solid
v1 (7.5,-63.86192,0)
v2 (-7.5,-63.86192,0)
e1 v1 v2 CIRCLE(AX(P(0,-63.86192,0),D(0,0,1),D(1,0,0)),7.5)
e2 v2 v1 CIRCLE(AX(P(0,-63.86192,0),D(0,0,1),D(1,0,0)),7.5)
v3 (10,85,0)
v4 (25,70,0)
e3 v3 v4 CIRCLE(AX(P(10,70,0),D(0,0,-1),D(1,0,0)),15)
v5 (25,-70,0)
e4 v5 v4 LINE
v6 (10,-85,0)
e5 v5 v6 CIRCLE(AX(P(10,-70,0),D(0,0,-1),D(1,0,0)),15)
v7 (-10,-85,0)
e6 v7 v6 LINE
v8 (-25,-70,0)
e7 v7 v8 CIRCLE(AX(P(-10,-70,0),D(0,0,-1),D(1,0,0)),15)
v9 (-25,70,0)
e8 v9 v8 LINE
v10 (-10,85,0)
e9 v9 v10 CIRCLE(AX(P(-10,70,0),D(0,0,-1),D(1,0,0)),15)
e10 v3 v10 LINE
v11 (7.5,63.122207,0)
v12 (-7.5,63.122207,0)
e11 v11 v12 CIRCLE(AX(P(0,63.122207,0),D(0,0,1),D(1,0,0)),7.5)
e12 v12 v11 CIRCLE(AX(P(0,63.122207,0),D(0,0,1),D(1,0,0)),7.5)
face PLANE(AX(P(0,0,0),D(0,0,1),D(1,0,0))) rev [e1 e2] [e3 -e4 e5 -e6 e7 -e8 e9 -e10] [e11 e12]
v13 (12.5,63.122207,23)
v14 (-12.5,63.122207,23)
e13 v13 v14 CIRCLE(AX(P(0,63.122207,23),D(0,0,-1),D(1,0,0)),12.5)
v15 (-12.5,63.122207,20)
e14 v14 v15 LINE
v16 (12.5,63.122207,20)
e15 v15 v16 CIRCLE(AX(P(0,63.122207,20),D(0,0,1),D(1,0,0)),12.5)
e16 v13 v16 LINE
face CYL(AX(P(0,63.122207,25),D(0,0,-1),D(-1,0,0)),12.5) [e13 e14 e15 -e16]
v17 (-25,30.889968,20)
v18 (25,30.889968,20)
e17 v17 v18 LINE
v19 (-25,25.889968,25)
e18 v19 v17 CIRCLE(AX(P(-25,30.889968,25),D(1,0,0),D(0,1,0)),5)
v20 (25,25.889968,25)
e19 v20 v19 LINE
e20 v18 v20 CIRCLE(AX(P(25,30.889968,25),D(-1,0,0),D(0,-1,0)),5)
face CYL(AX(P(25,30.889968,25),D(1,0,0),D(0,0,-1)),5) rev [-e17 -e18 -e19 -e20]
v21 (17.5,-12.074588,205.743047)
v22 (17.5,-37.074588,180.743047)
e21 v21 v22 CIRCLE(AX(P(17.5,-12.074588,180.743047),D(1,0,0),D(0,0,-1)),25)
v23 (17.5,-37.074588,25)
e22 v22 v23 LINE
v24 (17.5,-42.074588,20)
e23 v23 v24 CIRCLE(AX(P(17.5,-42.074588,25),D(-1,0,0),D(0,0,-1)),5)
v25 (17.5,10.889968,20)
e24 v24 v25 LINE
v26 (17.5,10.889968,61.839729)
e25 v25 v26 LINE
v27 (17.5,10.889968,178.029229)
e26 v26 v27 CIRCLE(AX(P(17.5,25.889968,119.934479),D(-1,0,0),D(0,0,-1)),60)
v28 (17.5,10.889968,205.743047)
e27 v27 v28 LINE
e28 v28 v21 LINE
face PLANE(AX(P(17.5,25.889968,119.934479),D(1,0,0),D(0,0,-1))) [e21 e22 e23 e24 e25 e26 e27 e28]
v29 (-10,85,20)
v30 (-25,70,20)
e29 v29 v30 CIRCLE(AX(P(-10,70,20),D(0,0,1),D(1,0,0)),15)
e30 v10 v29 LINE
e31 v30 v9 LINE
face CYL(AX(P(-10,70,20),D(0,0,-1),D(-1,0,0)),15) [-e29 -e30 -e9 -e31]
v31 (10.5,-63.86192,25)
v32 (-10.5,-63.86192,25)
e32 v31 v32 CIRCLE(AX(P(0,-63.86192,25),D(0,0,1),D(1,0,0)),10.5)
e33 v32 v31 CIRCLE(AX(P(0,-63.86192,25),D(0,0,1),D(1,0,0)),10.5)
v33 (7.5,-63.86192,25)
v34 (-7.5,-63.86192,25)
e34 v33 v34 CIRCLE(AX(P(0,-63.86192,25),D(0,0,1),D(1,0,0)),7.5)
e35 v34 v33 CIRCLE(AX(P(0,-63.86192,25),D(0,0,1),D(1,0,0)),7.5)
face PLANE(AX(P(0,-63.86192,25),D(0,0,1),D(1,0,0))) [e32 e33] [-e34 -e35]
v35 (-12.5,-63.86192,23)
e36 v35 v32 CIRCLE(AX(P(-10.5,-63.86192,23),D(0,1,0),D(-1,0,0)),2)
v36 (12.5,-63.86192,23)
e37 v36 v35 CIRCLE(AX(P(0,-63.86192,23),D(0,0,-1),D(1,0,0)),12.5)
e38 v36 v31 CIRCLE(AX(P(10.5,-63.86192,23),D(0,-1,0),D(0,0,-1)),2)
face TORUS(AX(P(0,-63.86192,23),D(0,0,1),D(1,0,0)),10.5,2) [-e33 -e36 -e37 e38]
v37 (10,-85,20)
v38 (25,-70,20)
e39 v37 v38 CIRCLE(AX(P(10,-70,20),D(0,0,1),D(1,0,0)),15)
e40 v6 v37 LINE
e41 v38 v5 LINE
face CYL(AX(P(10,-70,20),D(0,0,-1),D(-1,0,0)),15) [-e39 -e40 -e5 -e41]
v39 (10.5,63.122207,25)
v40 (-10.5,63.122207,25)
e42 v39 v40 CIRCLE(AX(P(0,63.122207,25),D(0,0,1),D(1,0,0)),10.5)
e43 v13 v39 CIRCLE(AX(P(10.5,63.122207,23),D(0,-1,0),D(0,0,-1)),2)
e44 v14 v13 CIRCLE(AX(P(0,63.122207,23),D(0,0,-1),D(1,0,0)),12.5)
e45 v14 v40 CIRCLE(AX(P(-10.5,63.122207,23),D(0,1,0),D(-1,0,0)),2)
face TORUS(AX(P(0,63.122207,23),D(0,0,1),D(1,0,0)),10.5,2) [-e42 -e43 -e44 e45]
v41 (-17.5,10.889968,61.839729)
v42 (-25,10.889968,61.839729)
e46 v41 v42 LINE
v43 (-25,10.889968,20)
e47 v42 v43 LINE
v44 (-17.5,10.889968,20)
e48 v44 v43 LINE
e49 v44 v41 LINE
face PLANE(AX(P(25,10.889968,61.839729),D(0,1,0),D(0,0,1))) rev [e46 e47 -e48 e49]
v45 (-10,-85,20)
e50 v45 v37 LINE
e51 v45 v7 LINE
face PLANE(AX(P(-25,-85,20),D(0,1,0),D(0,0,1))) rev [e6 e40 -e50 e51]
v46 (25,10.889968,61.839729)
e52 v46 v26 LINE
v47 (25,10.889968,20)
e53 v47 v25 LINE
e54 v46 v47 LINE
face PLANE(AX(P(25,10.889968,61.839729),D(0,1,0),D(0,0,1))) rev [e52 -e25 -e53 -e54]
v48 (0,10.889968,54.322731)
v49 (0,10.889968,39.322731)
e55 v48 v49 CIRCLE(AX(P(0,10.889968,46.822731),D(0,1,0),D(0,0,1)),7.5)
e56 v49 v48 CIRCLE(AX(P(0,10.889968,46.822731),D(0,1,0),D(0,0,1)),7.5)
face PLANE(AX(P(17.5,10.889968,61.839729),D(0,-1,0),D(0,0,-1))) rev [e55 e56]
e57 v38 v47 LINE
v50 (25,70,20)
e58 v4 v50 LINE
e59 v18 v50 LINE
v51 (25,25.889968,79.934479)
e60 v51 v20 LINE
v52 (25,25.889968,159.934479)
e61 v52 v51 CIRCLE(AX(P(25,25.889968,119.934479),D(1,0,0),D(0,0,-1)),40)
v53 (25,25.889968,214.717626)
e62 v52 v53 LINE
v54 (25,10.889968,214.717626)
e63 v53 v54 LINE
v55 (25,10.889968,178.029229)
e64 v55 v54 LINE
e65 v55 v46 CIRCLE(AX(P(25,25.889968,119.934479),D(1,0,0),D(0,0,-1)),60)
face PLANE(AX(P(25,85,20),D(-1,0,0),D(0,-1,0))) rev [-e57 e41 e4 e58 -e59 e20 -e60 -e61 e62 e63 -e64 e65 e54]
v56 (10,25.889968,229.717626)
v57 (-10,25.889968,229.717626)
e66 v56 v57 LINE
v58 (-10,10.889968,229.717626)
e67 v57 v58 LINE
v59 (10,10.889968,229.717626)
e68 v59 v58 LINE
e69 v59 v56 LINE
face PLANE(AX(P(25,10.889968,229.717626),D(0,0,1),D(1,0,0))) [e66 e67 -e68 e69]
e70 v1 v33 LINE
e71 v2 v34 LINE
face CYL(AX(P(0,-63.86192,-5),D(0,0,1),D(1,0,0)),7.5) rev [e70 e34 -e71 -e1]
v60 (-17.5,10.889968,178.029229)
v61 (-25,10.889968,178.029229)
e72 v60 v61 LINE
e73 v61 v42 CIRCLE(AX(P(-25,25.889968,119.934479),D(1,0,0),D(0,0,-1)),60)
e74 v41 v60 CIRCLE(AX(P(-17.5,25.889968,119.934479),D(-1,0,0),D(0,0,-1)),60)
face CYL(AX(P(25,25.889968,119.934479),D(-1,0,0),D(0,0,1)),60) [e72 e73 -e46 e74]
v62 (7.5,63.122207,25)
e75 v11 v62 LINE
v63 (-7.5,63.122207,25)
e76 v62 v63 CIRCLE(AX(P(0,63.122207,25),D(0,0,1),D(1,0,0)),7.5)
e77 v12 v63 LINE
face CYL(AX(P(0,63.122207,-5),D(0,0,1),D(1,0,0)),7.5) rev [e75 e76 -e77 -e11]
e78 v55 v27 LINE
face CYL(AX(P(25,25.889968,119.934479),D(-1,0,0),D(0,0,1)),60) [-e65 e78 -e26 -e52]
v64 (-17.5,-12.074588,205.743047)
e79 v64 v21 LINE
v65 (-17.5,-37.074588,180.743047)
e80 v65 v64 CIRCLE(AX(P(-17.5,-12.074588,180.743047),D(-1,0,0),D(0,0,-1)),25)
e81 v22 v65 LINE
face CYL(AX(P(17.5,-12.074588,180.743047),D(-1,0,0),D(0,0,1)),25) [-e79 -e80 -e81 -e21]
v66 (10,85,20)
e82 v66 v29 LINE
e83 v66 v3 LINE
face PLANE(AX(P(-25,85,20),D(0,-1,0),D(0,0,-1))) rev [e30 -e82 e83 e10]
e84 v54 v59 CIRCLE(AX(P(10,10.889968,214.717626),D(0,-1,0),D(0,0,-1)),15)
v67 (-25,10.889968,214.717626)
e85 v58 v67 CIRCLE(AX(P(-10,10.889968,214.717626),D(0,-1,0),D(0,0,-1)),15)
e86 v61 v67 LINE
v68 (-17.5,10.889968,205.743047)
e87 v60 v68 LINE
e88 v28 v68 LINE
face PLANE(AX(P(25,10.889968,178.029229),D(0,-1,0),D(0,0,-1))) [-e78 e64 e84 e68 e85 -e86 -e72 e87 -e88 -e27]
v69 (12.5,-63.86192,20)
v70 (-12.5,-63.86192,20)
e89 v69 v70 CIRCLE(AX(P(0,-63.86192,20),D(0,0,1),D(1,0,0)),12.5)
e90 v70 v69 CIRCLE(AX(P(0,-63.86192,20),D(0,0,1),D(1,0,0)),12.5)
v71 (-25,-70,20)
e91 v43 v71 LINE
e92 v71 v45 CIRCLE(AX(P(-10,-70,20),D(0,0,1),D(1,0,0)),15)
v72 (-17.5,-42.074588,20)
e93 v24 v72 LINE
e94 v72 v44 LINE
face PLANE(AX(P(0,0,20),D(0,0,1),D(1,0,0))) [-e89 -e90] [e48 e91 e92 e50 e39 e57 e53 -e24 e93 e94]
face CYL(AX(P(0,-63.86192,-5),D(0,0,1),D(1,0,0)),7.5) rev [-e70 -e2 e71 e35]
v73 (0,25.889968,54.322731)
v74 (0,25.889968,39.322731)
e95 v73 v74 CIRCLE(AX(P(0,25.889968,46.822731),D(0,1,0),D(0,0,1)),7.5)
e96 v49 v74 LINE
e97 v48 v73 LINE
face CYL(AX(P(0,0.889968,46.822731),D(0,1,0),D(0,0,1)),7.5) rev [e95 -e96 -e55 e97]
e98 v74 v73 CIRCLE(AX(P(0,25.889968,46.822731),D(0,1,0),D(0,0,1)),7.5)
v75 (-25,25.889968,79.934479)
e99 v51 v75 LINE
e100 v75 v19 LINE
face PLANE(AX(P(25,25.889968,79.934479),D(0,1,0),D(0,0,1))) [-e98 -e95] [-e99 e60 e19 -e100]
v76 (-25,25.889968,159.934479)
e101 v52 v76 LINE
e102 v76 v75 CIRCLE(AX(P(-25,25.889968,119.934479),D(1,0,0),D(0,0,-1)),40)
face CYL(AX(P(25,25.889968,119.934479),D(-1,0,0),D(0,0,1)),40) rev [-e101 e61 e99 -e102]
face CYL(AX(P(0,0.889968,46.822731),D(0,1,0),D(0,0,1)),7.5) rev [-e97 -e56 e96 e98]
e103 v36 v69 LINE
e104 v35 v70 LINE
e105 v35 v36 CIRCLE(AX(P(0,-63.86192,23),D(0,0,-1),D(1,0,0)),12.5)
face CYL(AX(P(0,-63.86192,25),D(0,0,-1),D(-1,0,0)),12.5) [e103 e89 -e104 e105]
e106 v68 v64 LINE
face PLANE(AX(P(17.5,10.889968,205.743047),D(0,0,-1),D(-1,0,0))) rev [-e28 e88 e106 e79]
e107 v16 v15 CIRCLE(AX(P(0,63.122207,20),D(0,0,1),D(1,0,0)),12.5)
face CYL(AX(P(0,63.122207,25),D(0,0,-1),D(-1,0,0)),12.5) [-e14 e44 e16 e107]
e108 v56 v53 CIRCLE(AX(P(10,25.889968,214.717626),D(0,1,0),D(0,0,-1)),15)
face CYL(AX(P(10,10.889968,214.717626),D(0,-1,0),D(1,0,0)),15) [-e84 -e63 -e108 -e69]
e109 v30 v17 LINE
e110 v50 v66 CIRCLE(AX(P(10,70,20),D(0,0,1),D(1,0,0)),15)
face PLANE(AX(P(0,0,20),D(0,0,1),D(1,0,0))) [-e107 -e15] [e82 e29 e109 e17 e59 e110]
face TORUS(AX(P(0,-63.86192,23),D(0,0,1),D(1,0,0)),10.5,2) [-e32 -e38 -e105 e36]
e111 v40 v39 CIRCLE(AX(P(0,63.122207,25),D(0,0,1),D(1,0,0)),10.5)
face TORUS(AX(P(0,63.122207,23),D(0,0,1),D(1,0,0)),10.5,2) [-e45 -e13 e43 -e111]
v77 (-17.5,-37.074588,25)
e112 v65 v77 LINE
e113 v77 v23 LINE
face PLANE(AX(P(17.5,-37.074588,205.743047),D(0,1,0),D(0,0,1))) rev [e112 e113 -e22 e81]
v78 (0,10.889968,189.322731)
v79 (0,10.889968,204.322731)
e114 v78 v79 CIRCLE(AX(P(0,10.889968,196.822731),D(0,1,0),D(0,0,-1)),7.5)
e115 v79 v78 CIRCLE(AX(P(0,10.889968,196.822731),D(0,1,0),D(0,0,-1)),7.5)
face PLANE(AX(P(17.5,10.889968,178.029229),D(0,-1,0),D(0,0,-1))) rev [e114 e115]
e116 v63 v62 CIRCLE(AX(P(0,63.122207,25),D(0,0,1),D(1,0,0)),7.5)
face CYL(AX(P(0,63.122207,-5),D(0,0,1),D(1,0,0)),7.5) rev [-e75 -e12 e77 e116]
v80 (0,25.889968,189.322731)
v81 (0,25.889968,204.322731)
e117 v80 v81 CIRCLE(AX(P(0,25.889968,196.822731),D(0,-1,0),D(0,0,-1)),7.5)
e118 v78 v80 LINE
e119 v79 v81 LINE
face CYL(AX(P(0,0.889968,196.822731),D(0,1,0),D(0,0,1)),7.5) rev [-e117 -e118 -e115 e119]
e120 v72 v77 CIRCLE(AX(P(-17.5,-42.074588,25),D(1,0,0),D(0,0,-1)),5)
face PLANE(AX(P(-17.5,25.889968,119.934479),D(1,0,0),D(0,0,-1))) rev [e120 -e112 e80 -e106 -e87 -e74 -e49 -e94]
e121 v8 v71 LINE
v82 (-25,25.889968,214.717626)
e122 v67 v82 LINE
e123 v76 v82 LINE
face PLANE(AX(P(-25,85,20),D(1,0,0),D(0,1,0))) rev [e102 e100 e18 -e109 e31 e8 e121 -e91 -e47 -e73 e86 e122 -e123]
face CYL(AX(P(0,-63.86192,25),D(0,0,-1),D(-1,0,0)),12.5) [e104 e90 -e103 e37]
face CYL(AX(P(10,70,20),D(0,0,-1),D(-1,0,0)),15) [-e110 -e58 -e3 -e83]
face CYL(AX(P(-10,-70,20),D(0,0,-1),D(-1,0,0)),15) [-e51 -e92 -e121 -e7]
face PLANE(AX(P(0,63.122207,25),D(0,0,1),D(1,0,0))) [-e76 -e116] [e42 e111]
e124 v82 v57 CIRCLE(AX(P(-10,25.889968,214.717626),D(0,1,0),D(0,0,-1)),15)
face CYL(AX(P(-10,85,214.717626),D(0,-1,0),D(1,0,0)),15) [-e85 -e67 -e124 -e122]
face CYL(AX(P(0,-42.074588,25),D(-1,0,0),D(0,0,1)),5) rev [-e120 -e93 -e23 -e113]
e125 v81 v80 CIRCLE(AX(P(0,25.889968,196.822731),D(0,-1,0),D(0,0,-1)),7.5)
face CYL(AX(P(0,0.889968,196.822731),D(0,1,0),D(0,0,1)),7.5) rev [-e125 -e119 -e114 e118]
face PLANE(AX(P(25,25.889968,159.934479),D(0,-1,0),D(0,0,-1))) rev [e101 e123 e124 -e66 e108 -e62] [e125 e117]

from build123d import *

# Parameters (mm, degrees)
BASE_PLATE_SKETCH_W             = 50
BASE_PLATE_SKETCH_H             = 170
BASE_PLATE_170X50X20_DEPTH      = 20
CLAMP_SADDLE_DEPTH              = 25
SADDLE_FILLET_R15_R             = 15
SADDLE_TO_PLATE_FILLET_R5_R     = 5
CLAMP_BOLT_HOLES_SKETCH_R       = 7.5
CLAMP_BOLT_HOLES_2X_15_DEPTH    = 25
MOUNTING_HOLES_SKETCH_R         = 7.5
MOUNTING_HOLES_2X_15_DEPTH      = 25
MOUNTING_START                  = 5
MOUNTING_HOLE_BOSSES_SKETCH_R   = 12.5
MOUNTING_HOLE_BOSSES_SKETCH_R_2 = 7.5
MOUNTING_HOLE_BOSSES_25_DEPTH   = 5
HOLE_BOSS_FILLET_R2_R           = 2
BASE_PLATE_CORNER_FILLETS_R15_R = 15
SUPPORT_RIB_DEPTH               = 17.5
SUPPORT_RIB_FILLET_R25_R        = 25
RIB_TO_PLATE_FILLET_R5_R        = 5


with BuildPart() as part:
    # Base Plate Sketch → Base Plate 170x50x20 (new body)
    with BuildSketch(Plane.XY):
        Rectangle(BASE_PLATE_SKETCH_W, BASE_PLATE_SKETCH_H)
    extrude(amount=BASE_PLATE_170X50X20_DEPTH)

    # Clamp Saddle Sketch → Clamp Saddle (add, symmetric)
    with BuildSketch(Plane(origin=(0, 0, 0), x_dir=(0, 0, -1), z_dir=(1, 0, 0))):
        with BuildLine():
            Line((-159.934479129, 25.889967638), (-179.934479129, 25.889967638))
            Line((-179.934479129, 25.889967638), (-229.717625742, 25.889967638))
            Line((-229.717625742, 25.889967638), (-229.717625742, 10.889967638))
            Line((-229.717625742, 10.889967638), (-178.029229322, 10.889967638))
            ThreePointArc((-178.029229322, 10.889967638), (-119.934479129, -34.110032362), (-61.839728936, 10.889967638))
            Line((-61.839728936, 10.889967638), (-20, 10.889967638))
            Line((-20, 10.889967638), (-20, 25.889967638))
            Line((-20, 25.889967638), (-79.934479129, 25.889967638))
            ThreePointArc((-79.934479129, 25.889967638), (-119.934479129, -14.110032362), (-159.934479129, 25.889967638))
        make_face()
    extrude(amount=CLAMP_SADDLE_DEPTH, both=True)

    # Saddle Fillet R15
    saddle_fillet_r15_edges = [part.edges().sort_by_distance(p)[0] for p in [
        (25, 18.389967638, 229.717625742),
        (-25, 18.389967638, 229.717625742),
    ]]
    fillet(saddle_fillet_r15_edges, radius=SADDLE_FILLET_R15_R)

    # Saddle To Plate Fillet R5
    saddle_to_plate_fillet_r5_edges = [part.edges().sort_by_distance(p)[0] for p in [
        (0, 25.889967638, 20),
    ]]
    fillet(saddle_to_plate_fillet_r5_edges, radius=SADDLE_TO_PLATE_FILLET_R5_R)

    # Clamp Bolt Holes Sketch → Clamp Bolt Holes 2xØ15 (cut, symmetric)
    with BuildSketch(Plane(origin=(0, 25.889967638, 0), x_dir=(1, 0, 0), z_dir=(0, 1, 0))):
        with Locations(Location((0, -46.822731441, 0), (0, 0, 270))):
            Circle(CLAMP_BOLT_HOLES_SKETCH_R)
        with Locations(Location((0, -196.822731441, 0), (0, 0, 90))):
            Circle(CLAMP_BOLT_HOLES_SKETCH_R)
    extrude(amount=CLAMP_BOLT_HOLES_2X_15_DEPTH, both=True, mode=Mode.SUBTRACT)

    # Mounting Holes Sketch → Mounting Holes 2xØ15 (cut, symmetric)
    with BuildSketch(Plane.XY.offset(20)):
        with Locations((0, 63.122206812)):
            Circle(MOUNTING_HOLES_SKETCH_R)
        with Locations((0, -63.861920173)):
            Circle(MOUNTING_HOLES_SKETCH_R)
    extrude(amount=MOUNTING_HOLES_2X_15_DEPTH, both=True, mode=Mode.SUBTRACT)

    # Mounting Hole Bosses Sketch → Mounting Hole Bosses Ø25 (add)
    # profile 1 of 2: a face of its own
    with BuildSketch(Plane.XY.offset(20).offset(MOUNTING_START)):
        with Locations((0, 63.122206812)):
            Circle(MOUNTING_HOLE_BOSSES_SKETCH_R)
        with Locations((0, 63.122206812)):
            Circle(MOUNTING_HOLE_BOSSES_SKETCH_R_2, mode=Mode.SUBTRACT)
    # profile 2 of 2: a face of its own
    with BuildSketch(Plane.XY.offset(20).offset(MOUNTING_START)):
        with Locations((0, -63.861920173)):
            Circle(MOUNTING_HOLE_BOSSES_SKETCH_R)
        with Locations((0, -63.861920173)):
            Circle(MOUNTING_HOLE_BOSSES_SKETCH_R_2, mode=Mode.SUBTRACT)
    extrude(amount=-MOUNTING_HOLE_BOSSES_25_DEPTH)

    # Hole Boss Fillet R2
    hole_boss_fillet_r2_edges = [part.edges().sort_by_distance(p)[0] for p in [
        (-12.5, 63.122206812, 25),
        (-12.5, -63.861920173, 25),
    ]]
    fillet(hole_boss_fillet_r2_edges, radius=HOLE_BOSS_FILLET_R2_R)

    # Base Plate Corner Fillets R15
    base_plate_corner_fillets_r15_edges = [part.edges().sort_by_distance(p)[0] for p in [
        (25, -85, 10),
        (-25, -85, 10),
        (-25, 85, 10),
        (25, 85, 10),
    ]]
    fillet(base_plate_corner_fillets_r15_edges, radius=BASE_PLATE_CORNER_FILLETS_R15_R)

    # Support Rib Sketch → Support Rib (add, symmetric)
    with BuildSketch(Plane(origin=(0, 0, 0), x_dir=(0, 0, -1), z_dir=(1, 0, 0))):
        with BuildLine():
            Line((-205.743047043, 10.889967638), (-205.743047043, -37.074588444))
            Line((-205.743047043, -37.074588444), (-20, -37.074588444))
            Line((-20, -37.074588444), (-20, 10.889967638))
            Line((-20, 10.889967638), (-61.839728936, 10.889967638))
            ThreePointArc((-61.839728936, 10.889967638), (-119.934479129, -34.110032362), (-178.029229322, 10.889967638))
            Line((-178.029229322, 10.889967638), (-205.743047043, 10.889967638))
        make_face()
    extrude(amount=SUPPORT_RIB_DEPTH, both=True)

    # Support Rib Fillet R25
    support_rib_fillet_r25_edges = [part.edges().sort_by_distance(p)[0] for p in [
        (0, -37.074588444, 205.743047043),
    ]]
    fillet(support_rib_fillet_r25_edges, radius=SUPPORT_RIB_FILLET_R25_R)

    # Rib To Plate Fillet R5
    rib_to_plate_fillet_r5_edges = [part.edges().sort_by_distance(p)[0] for p in [
        (0, -37.074588444, 20),
    ]]
    fillet(rib_to_plate_fillet_r5_edges, radius=RIB_TO_PLATE_FILLET_R5_R)


solid = part.part
